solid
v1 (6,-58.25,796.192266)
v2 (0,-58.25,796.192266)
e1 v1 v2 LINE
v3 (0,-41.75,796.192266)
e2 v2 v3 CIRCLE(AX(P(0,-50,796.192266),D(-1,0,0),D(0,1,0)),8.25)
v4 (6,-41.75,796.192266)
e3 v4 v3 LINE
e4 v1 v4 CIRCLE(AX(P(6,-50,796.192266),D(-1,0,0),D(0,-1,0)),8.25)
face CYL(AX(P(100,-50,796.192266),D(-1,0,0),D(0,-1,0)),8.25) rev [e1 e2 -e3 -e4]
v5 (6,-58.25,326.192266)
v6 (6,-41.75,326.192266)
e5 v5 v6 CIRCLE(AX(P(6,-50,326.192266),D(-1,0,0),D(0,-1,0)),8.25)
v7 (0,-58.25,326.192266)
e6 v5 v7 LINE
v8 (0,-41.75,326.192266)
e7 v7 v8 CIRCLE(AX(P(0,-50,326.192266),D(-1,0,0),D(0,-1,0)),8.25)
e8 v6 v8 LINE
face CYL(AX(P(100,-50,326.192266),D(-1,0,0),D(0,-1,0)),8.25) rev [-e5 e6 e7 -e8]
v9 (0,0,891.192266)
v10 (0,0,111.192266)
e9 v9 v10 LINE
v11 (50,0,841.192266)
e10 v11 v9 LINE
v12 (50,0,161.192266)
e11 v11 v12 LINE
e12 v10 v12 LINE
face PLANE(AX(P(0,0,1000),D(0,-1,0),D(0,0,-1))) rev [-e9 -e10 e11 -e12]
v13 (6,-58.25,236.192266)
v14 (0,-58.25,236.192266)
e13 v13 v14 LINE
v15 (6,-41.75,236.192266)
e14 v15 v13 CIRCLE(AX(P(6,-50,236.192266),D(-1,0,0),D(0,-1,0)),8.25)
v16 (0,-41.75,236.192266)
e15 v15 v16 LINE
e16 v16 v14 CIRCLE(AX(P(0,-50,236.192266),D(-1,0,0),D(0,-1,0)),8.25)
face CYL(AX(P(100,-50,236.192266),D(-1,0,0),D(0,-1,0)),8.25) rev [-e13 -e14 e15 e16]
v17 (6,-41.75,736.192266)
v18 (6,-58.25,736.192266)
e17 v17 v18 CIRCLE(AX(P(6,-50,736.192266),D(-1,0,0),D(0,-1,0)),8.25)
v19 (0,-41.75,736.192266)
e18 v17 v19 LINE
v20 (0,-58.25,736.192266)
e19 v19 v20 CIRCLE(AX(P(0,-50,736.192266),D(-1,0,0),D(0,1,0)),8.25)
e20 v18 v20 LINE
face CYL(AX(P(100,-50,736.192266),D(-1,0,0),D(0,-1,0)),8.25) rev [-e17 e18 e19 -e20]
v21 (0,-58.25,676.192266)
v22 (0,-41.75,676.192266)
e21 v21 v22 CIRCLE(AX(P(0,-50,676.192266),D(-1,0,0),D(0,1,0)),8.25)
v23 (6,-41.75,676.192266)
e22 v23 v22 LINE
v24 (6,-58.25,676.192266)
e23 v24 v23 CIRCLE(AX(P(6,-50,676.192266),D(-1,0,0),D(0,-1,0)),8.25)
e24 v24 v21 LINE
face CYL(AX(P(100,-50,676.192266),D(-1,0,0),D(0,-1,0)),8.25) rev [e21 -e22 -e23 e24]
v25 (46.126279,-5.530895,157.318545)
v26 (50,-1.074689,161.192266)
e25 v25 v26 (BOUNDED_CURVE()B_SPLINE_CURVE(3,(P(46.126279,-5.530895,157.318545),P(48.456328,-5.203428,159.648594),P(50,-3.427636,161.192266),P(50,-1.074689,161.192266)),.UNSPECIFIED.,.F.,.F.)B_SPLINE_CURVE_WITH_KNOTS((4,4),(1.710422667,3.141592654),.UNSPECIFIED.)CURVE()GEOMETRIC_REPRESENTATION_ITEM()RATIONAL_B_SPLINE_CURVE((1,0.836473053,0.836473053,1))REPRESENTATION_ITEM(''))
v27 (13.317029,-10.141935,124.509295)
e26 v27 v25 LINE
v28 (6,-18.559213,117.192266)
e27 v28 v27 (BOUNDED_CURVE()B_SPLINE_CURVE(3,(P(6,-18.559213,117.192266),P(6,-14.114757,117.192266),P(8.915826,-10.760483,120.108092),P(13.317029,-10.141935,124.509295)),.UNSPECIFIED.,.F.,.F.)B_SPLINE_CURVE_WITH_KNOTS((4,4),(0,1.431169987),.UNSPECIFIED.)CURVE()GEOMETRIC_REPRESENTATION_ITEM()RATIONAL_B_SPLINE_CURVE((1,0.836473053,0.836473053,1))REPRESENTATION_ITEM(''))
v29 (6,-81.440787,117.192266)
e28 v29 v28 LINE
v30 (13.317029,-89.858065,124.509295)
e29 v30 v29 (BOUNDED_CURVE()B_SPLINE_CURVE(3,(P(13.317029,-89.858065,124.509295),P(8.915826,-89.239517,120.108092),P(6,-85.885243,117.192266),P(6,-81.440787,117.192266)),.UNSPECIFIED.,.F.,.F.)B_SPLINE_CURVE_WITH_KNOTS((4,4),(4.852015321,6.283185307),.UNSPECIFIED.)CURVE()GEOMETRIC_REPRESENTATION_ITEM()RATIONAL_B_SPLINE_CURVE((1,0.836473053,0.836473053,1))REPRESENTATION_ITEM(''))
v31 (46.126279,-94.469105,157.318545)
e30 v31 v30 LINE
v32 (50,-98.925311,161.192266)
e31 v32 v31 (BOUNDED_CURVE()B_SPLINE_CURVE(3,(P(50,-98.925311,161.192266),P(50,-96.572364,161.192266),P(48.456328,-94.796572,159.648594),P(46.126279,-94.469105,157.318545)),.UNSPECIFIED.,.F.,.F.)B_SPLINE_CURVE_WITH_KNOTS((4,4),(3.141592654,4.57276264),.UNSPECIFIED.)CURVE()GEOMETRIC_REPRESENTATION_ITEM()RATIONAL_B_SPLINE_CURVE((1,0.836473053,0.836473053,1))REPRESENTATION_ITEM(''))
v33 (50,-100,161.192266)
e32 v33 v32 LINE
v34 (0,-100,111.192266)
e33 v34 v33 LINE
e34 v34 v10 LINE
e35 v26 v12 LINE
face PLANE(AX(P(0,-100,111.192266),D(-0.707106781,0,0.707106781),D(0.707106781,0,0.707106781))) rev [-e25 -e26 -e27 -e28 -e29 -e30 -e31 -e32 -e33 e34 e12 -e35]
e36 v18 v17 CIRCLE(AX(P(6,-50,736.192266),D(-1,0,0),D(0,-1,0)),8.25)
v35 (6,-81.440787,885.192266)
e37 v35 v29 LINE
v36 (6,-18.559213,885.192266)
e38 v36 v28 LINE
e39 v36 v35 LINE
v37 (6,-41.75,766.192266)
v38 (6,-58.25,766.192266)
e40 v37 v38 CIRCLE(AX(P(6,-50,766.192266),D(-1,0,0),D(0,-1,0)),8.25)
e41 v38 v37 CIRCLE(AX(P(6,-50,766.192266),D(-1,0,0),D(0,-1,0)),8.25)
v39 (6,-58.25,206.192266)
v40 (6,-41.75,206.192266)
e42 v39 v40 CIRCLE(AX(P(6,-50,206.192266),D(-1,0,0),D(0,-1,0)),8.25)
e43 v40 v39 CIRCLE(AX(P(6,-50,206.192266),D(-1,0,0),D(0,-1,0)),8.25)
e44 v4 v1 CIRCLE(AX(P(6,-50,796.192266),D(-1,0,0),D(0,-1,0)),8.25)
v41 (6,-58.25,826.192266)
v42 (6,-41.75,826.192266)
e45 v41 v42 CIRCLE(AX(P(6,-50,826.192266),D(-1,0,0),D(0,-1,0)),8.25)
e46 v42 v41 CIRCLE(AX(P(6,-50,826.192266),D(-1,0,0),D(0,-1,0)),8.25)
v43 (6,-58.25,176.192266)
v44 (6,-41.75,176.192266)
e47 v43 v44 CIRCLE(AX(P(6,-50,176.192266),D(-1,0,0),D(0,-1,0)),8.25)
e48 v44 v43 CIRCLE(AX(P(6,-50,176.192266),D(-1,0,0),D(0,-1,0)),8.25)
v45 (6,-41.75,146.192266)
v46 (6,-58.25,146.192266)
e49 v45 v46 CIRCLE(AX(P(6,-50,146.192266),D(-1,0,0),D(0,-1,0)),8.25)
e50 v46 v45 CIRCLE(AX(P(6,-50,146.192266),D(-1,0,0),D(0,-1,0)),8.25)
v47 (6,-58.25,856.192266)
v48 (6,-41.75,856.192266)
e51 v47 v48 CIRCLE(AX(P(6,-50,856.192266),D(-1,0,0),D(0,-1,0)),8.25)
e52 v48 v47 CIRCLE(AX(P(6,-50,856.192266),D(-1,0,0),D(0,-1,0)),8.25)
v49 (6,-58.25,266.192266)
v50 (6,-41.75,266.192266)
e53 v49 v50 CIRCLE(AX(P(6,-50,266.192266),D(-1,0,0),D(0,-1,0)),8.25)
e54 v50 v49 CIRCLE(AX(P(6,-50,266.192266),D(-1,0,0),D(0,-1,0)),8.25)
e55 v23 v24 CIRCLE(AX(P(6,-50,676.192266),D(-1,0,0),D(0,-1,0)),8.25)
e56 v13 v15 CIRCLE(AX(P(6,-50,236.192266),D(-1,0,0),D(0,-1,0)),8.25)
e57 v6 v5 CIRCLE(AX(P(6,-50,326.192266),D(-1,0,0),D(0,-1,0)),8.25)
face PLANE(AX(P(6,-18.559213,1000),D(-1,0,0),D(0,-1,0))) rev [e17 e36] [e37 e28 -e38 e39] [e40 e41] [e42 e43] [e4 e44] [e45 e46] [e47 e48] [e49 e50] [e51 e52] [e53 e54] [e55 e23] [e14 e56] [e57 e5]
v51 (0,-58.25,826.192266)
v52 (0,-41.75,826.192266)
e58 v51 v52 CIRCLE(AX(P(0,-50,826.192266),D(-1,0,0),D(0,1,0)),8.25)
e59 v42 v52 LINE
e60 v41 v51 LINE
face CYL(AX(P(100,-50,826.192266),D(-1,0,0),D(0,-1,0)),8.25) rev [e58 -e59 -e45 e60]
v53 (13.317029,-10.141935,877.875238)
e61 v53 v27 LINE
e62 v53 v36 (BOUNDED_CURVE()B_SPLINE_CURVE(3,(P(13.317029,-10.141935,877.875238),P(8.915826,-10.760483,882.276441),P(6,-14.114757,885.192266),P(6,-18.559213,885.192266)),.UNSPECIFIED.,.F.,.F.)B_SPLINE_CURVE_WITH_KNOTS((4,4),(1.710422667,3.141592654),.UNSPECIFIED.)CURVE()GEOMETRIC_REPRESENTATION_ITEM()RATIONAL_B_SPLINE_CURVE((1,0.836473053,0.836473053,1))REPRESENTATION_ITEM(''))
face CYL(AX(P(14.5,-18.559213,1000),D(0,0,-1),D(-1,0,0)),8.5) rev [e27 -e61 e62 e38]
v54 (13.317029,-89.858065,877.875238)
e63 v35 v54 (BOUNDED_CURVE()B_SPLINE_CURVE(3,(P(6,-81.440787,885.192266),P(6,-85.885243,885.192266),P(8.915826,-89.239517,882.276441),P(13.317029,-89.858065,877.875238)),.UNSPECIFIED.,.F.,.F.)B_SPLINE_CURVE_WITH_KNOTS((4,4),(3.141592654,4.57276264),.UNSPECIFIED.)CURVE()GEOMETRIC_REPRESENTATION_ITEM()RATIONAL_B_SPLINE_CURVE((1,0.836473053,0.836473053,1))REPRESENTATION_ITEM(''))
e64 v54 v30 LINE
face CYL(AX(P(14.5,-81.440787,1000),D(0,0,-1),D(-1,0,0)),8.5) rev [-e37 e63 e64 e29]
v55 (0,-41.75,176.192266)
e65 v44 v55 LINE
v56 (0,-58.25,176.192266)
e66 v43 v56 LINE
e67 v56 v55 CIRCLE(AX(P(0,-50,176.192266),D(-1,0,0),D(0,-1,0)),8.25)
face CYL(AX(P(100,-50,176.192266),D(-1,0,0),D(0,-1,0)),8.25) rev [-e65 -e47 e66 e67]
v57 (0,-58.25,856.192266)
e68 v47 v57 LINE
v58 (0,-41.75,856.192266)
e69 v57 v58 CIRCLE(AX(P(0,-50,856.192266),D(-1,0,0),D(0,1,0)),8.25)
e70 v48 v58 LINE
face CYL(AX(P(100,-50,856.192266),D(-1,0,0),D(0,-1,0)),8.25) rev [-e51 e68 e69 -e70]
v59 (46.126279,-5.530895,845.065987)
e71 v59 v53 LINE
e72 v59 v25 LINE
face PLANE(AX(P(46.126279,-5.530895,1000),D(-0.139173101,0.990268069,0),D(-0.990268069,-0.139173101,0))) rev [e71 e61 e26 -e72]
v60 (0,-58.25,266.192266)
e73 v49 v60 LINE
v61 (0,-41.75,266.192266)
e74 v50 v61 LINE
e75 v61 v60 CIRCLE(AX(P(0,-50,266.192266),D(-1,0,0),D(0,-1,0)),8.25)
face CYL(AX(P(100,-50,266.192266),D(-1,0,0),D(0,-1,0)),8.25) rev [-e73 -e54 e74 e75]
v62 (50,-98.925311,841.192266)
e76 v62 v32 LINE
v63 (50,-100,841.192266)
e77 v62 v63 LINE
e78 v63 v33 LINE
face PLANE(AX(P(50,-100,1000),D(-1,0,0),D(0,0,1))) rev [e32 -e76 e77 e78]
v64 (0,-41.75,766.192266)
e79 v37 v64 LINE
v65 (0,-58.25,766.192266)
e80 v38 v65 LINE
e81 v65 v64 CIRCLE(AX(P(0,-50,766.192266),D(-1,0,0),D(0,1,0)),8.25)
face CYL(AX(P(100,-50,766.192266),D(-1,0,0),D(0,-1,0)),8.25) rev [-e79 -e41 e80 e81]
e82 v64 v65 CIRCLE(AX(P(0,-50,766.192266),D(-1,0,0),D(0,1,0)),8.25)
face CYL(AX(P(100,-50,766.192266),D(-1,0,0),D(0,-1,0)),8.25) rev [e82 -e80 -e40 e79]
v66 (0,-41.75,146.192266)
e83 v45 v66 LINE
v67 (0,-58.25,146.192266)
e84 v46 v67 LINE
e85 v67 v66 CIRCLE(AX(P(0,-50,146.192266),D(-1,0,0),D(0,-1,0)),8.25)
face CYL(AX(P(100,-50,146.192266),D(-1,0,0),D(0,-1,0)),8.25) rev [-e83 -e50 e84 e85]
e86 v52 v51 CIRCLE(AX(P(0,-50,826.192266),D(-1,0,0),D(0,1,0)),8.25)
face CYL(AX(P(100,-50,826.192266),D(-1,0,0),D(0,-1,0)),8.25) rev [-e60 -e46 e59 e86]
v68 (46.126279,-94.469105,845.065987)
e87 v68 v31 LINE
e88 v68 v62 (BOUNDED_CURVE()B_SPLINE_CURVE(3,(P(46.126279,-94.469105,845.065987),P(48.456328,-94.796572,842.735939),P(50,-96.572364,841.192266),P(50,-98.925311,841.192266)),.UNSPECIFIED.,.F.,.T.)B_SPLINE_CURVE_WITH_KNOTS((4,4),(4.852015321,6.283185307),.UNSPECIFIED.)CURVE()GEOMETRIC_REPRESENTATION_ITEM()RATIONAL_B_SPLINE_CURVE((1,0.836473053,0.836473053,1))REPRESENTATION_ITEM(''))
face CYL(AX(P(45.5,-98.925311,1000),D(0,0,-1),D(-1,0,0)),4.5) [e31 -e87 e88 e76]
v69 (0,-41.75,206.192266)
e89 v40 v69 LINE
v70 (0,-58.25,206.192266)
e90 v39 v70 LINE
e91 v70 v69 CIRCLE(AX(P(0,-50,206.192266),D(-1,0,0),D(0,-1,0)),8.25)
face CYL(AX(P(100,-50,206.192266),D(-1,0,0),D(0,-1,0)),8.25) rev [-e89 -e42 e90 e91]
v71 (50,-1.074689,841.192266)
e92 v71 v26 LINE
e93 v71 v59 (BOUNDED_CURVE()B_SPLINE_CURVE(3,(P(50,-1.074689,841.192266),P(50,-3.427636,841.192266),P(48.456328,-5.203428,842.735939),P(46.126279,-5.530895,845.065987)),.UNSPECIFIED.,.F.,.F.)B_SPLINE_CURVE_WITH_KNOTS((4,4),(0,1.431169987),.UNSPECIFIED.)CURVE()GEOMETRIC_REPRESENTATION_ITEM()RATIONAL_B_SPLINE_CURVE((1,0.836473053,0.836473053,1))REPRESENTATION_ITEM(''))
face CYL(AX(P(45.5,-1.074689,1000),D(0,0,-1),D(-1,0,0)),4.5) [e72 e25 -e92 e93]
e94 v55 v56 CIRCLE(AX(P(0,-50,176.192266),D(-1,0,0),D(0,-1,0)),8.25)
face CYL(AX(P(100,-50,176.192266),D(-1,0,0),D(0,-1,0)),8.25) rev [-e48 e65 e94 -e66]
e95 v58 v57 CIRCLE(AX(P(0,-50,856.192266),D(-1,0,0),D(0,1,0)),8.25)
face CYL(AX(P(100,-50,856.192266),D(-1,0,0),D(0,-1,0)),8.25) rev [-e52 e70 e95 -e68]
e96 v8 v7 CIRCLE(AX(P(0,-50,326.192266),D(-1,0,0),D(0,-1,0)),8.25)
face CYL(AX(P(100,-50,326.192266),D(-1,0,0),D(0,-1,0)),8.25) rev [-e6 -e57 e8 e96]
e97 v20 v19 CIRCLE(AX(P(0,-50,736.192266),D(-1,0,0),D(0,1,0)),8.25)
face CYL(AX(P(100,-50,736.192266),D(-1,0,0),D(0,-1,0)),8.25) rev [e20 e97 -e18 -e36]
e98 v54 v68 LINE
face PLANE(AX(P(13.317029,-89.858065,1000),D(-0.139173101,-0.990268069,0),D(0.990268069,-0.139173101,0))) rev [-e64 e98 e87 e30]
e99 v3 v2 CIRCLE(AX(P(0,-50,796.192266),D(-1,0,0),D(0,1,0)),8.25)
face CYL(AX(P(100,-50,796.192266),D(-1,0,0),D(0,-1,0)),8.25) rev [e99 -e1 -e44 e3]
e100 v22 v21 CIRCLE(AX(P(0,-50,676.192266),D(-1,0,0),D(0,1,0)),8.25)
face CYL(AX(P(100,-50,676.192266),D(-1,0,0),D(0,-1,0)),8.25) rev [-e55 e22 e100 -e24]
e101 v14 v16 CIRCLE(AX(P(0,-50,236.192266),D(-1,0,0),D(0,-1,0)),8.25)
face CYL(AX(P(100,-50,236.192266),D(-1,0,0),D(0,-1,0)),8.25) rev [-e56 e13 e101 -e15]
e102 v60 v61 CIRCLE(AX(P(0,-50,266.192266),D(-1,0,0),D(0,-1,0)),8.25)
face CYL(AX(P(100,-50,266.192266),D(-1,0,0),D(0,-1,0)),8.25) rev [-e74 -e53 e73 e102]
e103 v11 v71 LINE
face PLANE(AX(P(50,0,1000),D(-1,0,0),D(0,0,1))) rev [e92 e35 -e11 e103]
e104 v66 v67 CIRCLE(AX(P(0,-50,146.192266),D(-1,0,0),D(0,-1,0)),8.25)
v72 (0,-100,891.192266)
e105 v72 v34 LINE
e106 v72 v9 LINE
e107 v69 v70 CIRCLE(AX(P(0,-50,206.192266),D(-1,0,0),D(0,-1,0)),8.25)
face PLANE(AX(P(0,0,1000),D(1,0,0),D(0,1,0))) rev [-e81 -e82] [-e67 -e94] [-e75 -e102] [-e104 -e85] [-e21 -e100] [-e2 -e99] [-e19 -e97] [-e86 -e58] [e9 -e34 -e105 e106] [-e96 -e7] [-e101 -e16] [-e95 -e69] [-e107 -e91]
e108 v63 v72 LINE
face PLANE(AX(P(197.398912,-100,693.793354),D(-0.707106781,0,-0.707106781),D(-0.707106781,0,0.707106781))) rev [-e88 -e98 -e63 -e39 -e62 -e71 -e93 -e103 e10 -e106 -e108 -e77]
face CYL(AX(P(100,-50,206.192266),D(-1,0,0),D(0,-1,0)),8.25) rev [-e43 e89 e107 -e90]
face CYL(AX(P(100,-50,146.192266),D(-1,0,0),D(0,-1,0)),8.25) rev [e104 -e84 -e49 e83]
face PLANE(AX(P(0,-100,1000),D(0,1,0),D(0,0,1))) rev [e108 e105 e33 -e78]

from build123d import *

# Parameters (mm, degrees)
BOSS_EXTRUDE1_DEPTH = 1000
CUT_EXTRUDE4_DEPTH  = 100
SKETCH6_R           = 8.25
CUT_EXTRUDE5_DEPTH  = 100


with BuildPart() as part:
    # Sketch1 → Boss-Extrude1 (new body)
    with BuildSketch(Plane.XY):
        with BuildLine():
            Line((0, 0), (0, -100))
            Line((0, -100), (50, -100))
            Line((50, -100), (50, -98.925311188))
            ThreePointArc((50, -98.925311188), (48.896193111, -95.973045557), (46.126278954, -94.469104878))
            Line((46.126278954, -94.469104878), (13.317028642, -89.858065454))
            ThreePointArc((13.317028642, -89.858065454), (8.084968568, -87.017288616), (6, -81.440786869))
            Line((6, -81.440786869), (6, -18.559213131))
            ThreePointArc((6, -18.559213131), (8.084968568, -12.982711384), (13.317028642, -10.141934546))
            Line((13.317028642, -10.141934546), (46.126278954, -5.530895122))
            ThreePointArc((46.126278954, -5.530895122), (48.896193111, -4.026954443), (50, -1.074688812))
            Line((50, -1.074688812), (50, 0))
            Line((50, 0), (0, 0))
        make_face()
    extrude(amount=BOSS_EXTRUDE1_DEPTH)

    # Sketch5 → Cut-Extrude4 (cut)
    with BuildSketch(Plane(origin=(0, 0, 0), x_dir=(1, 0, 0), z_dir=(0, 1, 0))):
        Polygon((0, -111.192266245), (155.007948876, -266.200215121), (155.007948876, 58.518788552), (-221.01044115, 43.925946333), align=None)
        Polygon((197.398911987, -693.793354258), (279.115957405, -1211.070261728), (0, -1168.351944778), (-115.400263834, -952.431807993), (0, -891.192266245), align=None)
    extrude(amount=-CUT_EXTRUDE4_DEPTH, mode=Mode.SUBTRACT)

    # Sketch6 → Cut-Extrude5 (cut)
    with BuildSketch(Plane.ZY):
        with Locations(Location((146.192266245, -50, 0), (0, 0, 270))):
            Circle(SKETCH6_R)
        with Locations(Location((176.192266245, -50, 0), (0, 0, 270))):
            Circle(SKETCH6_R)
        with Locations(Location((206.192266245, -50, 0), (0, 0, 270))):
            Circle(SKETCH6_R)
        with Locations(Location((236.192266245, -50, 0), (0, 0, 270))):
            Circle(SKETCH6_R)
        with Locations(Location((266.192266245, -50, 0), (0, 0, 270))):
            Circle(SKETCH6_R)
        with Locations(Location((326.192266245, -50, 0), (0, 0, 270))):
            Circle(SKETCH6_R)
        with Locations(Location((676.192266245, -50, 0), (0, 0, 270))):
            Circle(SKETCH6_R)
        with Locations(Location((736.192266245, -50, 0), (0, 0, 270))):
            Circle(SKETCH6_R)
        with Locations(Location((766.192266245, -50, 0), (0, 0, 270))):
            Circle(SKETCH6_R)
        with Locations(Location((796.192266245, -50, 0), (0, 0, 270))):
            Circle(SKETCH6_R)
        with Locations(Location((826.192266245, -50, 0), (0, 0, 270))):
            Circle(SKETCH6_R)
        with Locations(Location((856.192266245, -50, 0), (0, 0, 270))):
            Circle(SKETCH6_R)
    extrude(amount=-CUT_EXTRUDE5_DEPTH, mode=Mode.SUBTRACT)


solid = part.part
